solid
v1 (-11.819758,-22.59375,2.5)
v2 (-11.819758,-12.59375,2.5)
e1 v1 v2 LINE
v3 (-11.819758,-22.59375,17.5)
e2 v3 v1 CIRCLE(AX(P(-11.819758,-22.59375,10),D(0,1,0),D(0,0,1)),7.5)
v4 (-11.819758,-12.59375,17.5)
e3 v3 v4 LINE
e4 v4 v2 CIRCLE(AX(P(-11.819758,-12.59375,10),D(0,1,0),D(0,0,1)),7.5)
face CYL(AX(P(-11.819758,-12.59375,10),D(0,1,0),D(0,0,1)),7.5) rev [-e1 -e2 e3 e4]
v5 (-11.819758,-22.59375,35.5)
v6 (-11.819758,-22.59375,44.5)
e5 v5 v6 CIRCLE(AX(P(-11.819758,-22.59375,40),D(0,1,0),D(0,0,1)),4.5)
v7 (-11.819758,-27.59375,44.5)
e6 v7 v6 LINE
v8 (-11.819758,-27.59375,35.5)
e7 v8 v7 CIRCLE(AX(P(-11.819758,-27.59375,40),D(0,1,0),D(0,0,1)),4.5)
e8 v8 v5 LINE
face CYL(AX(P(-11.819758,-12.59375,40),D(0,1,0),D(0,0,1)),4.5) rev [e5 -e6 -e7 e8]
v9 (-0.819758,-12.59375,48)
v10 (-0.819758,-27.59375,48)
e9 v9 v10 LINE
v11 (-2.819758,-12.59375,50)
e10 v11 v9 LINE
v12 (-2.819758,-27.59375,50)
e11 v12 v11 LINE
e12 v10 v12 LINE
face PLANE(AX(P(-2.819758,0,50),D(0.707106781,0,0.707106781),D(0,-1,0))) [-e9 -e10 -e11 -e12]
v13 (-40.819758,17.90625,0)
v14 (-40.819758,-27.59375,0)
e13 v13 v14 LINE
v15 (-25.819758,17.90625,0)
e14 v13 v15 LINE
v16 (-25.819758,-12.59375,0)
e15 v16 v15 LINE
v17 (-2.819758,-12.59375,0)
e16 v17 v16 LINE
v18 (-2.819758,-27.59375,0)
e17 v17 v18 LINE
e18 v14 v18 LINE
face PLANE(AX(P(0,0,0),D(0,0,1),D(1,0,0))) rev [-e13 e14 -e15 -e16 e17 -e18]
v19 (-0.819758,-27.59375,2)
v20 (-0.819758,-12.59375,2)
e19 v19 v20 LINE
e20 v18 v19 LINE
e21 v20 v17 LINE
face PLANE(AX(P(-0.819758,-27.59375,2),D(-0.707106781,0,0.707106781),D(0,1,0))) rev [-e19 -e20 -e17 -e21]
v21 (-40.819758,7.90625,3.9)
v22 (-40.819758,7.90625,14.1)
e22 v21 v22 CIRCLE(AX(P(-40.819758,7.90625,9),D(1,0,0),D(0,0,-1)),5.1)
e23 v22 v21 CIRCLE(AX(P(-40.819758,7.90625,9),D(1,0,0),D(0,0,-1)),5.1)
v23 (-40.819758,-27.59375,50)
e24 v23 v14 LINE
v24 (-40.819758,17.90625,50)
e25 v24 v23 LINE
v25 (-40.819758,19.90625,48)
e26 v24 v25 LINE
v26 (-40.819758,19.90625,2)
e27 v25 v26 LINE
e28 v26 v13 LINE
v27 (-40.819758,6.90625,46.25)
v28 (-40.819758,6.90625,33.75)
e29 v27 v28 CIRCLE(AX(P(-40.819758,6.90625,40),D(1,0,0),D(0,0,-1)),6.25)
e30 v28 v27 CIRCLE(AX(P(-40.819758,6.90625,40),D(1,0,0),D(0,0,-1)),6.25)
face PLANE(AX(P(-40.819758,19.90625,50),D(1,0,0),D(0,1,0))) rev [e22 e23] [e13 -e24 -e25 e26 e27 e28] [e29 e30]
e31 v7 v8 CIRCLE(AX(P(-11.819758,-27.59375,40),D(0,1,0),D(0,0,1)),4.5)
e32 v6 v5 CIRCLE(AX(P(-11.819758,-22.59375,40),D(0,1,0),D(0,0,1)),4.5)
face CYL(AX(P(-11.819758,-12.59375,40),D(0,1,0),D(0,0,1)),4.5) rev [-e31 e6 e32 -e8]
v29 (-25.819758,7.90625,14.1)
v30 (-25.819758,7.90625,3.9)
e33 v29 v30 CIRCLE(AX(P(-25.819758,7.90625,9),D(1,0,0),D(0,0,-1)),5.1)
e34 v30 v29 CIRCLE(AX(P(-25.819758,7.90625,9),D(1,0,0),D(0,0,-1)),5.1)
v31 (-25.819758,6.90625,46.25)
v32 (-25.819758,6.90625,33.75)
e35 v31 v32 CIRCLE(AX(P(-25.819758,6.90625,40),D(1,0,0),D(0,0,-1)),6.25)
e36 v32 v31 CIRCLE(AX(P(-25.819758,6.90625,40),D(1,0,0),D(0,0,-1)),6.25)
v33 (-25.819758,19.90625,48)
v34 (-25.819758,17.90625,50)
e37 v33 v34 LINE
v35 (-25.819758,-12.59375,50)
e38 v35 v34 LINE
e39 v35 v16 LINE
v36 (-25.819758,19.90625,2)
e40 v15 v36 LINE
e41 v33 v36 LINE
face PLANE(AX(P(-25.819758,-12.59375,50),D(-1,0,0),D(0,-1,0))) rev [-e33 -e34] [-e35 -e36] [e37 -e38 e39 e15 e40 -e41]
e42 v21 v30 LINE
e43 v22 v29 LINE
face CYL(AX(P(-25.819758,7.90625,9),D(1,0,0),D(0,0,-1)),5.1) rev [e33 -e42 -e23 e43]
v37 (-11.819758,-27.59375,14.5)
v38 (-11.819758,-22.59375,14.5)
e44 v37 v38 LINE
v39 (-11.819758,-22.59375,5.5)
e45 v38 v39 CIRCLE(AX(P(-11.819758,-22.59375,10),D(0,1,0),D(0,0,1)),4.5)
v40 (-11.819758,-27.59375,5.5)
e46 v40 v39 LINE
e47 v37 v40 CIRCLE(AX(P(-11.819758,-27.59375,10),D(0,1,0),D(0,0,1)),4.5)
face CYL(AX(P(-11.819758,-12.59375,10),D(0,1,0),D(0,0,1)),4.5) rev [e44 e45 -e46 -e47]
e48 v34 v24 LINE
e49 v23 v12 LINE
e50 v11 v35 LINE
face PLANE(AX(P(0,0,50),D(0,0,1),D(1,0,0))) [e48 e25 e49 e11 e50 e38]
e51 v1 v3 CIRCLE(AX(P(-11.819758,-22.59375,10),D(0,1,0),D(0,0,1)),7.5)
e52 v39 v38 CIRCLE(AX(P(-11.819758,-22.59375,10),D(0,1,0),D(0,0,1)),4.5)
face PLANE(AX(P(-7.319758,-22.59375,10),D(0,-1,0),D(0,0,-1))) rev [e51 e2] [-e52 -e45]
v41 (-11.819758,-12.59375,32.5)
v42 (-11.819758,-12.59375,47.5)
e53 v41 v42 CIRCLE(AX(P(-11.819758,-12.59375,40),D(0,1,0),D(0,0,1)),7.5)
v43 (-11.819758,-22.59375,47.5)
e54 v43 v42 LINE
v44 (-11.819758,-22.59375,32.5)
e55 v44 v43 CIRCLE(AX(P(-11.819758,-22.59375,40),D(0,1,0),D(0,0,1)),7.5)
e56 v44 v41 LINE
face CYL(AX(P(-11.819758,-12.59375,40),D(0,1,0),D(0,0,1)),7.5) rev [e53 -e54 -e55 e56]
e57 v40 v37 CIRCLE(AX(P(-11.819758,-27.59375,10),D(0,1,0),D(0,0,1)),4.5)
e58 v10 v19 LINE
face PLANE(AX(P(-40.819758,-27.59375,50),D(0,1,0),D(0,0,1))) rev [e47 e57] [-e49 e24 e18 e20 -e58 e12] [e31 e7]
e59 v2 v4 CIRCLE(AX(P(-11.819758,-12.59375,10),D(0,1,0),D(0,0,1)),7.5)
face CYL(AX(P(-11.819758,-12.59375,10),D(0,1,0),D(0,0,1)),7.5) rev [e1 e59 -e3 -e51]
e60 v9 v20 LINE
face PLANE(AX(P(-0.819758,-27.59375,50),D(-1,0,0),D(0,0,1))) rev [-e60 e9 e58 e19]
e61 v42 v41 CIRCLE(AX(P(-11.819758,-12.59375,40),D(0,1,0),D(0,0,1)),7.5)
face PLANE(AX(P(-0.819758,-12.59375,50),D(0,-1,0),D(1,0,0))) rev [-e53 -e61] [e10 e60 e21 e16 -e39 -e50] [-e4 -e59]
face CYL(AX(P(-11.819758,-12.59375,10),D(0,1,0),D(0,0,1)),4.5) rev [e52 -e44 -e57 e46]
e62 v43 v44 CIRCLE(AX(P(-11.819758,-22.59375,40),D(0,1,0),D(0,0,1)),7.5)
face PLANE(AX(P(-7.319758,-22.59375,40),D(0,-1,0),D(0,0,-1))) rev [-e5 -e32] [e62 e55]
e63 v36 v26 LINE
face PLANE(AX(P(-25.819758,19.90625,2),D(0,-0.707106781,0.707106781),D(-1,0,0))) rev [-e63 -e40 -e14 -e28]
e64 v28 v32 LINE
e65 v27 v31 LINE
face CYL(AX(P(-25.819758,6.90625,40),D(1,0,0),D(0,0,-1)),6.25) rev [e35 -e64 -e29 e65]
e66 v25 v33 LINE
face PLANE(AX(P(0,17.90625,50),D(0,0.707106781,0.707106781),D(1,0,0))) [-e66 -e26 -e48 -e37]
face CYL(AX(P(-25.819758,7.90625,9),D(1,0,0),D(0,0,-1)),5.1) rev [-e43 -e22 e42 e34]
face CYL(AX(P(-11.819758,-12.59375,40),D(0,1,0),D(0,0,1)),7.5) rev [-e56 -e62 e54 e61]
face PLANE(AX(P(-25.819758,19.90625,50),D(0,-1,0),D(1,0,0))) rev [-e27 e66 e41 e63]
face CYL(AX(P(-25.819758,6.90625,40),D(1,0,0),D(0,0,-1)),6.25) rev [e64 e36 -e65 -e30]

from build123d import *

# Parameters (mm, degrees)
BOSS_EXTRUDE1_DEPTH    = 50
CHAMFER2_SIZE          = 2
HOLE4_D                = 9
HOLE4_CBORE_D          = 15
HOLE4_CBORE_DEPTH      = 10
M14X1_5_TAPPED_HOLE1_D = 12.5
M12_TAPPED_HOLE1_D     = 10.2


with BuildPart() as part:
    # Sketch1 → Boss-Extrude1 (new body)
    with BuildSketch(Plane.XY):
        Polygon((-40.819758101, 19.90625), (-40.819758101, -27.59375), (-0.819758101, -27.59375), (-0.819758101, -12.59375), (-25.819758101, -12.59375), (-25.819758101, 19.90625), align=None)
    extrude(amount=BOSS_EXTRUDE1_DEPTH)

    # Chamfer2
    chamfer2_edges = [part.edges().sort_by_distance(p)[0] for p in [
        (-0.819758101, -20.09375, 50),
        (-33.319758101, 19.90625, 50),
        (-0.819758101, -20.09375, 0),
        (-33.319758101, 19.90625, 0),
    ]]
    chamfer(chamfer2_edges, length=CHAMFER2_SIZE)

    # Hole4 (through all)
    with Locations(Plane(origin=(0, -12.59375, 0), x_dir=(1, 0, 0), z_dir=(0, 1, 0))):
        with Locations((-11.819758101, -10), (-11.819758101, -40)):
            CounterBoreHole(HOLE4_D / 2, HOLE4_CBORE_D / 2, HOLE4_CBORE_DEPTH)

    # M14x1.5 Tapped Hole1 (through all)
    with Locations(Plane(origin=(-25.819758101, 0, 0), x_dir=(0, 0, -1), z_dir=(1, 0, 0))):
        with Locations((-40, 6.90625)):
            Hole(M14X1_5_TAPPED_HOLE1_D / 2)

    # M12 Tapped Hole1 (through all)
    with Locations(Plane(origin=(-25.819758101, 0, 0), x_dir=(0, 0, -1), z_dir=(1, 0, 0))):
        with Locations((-9, 7.90625)):
            Hole(M12_TAPPED_HOLE1_D / 2)


solid = part.part
